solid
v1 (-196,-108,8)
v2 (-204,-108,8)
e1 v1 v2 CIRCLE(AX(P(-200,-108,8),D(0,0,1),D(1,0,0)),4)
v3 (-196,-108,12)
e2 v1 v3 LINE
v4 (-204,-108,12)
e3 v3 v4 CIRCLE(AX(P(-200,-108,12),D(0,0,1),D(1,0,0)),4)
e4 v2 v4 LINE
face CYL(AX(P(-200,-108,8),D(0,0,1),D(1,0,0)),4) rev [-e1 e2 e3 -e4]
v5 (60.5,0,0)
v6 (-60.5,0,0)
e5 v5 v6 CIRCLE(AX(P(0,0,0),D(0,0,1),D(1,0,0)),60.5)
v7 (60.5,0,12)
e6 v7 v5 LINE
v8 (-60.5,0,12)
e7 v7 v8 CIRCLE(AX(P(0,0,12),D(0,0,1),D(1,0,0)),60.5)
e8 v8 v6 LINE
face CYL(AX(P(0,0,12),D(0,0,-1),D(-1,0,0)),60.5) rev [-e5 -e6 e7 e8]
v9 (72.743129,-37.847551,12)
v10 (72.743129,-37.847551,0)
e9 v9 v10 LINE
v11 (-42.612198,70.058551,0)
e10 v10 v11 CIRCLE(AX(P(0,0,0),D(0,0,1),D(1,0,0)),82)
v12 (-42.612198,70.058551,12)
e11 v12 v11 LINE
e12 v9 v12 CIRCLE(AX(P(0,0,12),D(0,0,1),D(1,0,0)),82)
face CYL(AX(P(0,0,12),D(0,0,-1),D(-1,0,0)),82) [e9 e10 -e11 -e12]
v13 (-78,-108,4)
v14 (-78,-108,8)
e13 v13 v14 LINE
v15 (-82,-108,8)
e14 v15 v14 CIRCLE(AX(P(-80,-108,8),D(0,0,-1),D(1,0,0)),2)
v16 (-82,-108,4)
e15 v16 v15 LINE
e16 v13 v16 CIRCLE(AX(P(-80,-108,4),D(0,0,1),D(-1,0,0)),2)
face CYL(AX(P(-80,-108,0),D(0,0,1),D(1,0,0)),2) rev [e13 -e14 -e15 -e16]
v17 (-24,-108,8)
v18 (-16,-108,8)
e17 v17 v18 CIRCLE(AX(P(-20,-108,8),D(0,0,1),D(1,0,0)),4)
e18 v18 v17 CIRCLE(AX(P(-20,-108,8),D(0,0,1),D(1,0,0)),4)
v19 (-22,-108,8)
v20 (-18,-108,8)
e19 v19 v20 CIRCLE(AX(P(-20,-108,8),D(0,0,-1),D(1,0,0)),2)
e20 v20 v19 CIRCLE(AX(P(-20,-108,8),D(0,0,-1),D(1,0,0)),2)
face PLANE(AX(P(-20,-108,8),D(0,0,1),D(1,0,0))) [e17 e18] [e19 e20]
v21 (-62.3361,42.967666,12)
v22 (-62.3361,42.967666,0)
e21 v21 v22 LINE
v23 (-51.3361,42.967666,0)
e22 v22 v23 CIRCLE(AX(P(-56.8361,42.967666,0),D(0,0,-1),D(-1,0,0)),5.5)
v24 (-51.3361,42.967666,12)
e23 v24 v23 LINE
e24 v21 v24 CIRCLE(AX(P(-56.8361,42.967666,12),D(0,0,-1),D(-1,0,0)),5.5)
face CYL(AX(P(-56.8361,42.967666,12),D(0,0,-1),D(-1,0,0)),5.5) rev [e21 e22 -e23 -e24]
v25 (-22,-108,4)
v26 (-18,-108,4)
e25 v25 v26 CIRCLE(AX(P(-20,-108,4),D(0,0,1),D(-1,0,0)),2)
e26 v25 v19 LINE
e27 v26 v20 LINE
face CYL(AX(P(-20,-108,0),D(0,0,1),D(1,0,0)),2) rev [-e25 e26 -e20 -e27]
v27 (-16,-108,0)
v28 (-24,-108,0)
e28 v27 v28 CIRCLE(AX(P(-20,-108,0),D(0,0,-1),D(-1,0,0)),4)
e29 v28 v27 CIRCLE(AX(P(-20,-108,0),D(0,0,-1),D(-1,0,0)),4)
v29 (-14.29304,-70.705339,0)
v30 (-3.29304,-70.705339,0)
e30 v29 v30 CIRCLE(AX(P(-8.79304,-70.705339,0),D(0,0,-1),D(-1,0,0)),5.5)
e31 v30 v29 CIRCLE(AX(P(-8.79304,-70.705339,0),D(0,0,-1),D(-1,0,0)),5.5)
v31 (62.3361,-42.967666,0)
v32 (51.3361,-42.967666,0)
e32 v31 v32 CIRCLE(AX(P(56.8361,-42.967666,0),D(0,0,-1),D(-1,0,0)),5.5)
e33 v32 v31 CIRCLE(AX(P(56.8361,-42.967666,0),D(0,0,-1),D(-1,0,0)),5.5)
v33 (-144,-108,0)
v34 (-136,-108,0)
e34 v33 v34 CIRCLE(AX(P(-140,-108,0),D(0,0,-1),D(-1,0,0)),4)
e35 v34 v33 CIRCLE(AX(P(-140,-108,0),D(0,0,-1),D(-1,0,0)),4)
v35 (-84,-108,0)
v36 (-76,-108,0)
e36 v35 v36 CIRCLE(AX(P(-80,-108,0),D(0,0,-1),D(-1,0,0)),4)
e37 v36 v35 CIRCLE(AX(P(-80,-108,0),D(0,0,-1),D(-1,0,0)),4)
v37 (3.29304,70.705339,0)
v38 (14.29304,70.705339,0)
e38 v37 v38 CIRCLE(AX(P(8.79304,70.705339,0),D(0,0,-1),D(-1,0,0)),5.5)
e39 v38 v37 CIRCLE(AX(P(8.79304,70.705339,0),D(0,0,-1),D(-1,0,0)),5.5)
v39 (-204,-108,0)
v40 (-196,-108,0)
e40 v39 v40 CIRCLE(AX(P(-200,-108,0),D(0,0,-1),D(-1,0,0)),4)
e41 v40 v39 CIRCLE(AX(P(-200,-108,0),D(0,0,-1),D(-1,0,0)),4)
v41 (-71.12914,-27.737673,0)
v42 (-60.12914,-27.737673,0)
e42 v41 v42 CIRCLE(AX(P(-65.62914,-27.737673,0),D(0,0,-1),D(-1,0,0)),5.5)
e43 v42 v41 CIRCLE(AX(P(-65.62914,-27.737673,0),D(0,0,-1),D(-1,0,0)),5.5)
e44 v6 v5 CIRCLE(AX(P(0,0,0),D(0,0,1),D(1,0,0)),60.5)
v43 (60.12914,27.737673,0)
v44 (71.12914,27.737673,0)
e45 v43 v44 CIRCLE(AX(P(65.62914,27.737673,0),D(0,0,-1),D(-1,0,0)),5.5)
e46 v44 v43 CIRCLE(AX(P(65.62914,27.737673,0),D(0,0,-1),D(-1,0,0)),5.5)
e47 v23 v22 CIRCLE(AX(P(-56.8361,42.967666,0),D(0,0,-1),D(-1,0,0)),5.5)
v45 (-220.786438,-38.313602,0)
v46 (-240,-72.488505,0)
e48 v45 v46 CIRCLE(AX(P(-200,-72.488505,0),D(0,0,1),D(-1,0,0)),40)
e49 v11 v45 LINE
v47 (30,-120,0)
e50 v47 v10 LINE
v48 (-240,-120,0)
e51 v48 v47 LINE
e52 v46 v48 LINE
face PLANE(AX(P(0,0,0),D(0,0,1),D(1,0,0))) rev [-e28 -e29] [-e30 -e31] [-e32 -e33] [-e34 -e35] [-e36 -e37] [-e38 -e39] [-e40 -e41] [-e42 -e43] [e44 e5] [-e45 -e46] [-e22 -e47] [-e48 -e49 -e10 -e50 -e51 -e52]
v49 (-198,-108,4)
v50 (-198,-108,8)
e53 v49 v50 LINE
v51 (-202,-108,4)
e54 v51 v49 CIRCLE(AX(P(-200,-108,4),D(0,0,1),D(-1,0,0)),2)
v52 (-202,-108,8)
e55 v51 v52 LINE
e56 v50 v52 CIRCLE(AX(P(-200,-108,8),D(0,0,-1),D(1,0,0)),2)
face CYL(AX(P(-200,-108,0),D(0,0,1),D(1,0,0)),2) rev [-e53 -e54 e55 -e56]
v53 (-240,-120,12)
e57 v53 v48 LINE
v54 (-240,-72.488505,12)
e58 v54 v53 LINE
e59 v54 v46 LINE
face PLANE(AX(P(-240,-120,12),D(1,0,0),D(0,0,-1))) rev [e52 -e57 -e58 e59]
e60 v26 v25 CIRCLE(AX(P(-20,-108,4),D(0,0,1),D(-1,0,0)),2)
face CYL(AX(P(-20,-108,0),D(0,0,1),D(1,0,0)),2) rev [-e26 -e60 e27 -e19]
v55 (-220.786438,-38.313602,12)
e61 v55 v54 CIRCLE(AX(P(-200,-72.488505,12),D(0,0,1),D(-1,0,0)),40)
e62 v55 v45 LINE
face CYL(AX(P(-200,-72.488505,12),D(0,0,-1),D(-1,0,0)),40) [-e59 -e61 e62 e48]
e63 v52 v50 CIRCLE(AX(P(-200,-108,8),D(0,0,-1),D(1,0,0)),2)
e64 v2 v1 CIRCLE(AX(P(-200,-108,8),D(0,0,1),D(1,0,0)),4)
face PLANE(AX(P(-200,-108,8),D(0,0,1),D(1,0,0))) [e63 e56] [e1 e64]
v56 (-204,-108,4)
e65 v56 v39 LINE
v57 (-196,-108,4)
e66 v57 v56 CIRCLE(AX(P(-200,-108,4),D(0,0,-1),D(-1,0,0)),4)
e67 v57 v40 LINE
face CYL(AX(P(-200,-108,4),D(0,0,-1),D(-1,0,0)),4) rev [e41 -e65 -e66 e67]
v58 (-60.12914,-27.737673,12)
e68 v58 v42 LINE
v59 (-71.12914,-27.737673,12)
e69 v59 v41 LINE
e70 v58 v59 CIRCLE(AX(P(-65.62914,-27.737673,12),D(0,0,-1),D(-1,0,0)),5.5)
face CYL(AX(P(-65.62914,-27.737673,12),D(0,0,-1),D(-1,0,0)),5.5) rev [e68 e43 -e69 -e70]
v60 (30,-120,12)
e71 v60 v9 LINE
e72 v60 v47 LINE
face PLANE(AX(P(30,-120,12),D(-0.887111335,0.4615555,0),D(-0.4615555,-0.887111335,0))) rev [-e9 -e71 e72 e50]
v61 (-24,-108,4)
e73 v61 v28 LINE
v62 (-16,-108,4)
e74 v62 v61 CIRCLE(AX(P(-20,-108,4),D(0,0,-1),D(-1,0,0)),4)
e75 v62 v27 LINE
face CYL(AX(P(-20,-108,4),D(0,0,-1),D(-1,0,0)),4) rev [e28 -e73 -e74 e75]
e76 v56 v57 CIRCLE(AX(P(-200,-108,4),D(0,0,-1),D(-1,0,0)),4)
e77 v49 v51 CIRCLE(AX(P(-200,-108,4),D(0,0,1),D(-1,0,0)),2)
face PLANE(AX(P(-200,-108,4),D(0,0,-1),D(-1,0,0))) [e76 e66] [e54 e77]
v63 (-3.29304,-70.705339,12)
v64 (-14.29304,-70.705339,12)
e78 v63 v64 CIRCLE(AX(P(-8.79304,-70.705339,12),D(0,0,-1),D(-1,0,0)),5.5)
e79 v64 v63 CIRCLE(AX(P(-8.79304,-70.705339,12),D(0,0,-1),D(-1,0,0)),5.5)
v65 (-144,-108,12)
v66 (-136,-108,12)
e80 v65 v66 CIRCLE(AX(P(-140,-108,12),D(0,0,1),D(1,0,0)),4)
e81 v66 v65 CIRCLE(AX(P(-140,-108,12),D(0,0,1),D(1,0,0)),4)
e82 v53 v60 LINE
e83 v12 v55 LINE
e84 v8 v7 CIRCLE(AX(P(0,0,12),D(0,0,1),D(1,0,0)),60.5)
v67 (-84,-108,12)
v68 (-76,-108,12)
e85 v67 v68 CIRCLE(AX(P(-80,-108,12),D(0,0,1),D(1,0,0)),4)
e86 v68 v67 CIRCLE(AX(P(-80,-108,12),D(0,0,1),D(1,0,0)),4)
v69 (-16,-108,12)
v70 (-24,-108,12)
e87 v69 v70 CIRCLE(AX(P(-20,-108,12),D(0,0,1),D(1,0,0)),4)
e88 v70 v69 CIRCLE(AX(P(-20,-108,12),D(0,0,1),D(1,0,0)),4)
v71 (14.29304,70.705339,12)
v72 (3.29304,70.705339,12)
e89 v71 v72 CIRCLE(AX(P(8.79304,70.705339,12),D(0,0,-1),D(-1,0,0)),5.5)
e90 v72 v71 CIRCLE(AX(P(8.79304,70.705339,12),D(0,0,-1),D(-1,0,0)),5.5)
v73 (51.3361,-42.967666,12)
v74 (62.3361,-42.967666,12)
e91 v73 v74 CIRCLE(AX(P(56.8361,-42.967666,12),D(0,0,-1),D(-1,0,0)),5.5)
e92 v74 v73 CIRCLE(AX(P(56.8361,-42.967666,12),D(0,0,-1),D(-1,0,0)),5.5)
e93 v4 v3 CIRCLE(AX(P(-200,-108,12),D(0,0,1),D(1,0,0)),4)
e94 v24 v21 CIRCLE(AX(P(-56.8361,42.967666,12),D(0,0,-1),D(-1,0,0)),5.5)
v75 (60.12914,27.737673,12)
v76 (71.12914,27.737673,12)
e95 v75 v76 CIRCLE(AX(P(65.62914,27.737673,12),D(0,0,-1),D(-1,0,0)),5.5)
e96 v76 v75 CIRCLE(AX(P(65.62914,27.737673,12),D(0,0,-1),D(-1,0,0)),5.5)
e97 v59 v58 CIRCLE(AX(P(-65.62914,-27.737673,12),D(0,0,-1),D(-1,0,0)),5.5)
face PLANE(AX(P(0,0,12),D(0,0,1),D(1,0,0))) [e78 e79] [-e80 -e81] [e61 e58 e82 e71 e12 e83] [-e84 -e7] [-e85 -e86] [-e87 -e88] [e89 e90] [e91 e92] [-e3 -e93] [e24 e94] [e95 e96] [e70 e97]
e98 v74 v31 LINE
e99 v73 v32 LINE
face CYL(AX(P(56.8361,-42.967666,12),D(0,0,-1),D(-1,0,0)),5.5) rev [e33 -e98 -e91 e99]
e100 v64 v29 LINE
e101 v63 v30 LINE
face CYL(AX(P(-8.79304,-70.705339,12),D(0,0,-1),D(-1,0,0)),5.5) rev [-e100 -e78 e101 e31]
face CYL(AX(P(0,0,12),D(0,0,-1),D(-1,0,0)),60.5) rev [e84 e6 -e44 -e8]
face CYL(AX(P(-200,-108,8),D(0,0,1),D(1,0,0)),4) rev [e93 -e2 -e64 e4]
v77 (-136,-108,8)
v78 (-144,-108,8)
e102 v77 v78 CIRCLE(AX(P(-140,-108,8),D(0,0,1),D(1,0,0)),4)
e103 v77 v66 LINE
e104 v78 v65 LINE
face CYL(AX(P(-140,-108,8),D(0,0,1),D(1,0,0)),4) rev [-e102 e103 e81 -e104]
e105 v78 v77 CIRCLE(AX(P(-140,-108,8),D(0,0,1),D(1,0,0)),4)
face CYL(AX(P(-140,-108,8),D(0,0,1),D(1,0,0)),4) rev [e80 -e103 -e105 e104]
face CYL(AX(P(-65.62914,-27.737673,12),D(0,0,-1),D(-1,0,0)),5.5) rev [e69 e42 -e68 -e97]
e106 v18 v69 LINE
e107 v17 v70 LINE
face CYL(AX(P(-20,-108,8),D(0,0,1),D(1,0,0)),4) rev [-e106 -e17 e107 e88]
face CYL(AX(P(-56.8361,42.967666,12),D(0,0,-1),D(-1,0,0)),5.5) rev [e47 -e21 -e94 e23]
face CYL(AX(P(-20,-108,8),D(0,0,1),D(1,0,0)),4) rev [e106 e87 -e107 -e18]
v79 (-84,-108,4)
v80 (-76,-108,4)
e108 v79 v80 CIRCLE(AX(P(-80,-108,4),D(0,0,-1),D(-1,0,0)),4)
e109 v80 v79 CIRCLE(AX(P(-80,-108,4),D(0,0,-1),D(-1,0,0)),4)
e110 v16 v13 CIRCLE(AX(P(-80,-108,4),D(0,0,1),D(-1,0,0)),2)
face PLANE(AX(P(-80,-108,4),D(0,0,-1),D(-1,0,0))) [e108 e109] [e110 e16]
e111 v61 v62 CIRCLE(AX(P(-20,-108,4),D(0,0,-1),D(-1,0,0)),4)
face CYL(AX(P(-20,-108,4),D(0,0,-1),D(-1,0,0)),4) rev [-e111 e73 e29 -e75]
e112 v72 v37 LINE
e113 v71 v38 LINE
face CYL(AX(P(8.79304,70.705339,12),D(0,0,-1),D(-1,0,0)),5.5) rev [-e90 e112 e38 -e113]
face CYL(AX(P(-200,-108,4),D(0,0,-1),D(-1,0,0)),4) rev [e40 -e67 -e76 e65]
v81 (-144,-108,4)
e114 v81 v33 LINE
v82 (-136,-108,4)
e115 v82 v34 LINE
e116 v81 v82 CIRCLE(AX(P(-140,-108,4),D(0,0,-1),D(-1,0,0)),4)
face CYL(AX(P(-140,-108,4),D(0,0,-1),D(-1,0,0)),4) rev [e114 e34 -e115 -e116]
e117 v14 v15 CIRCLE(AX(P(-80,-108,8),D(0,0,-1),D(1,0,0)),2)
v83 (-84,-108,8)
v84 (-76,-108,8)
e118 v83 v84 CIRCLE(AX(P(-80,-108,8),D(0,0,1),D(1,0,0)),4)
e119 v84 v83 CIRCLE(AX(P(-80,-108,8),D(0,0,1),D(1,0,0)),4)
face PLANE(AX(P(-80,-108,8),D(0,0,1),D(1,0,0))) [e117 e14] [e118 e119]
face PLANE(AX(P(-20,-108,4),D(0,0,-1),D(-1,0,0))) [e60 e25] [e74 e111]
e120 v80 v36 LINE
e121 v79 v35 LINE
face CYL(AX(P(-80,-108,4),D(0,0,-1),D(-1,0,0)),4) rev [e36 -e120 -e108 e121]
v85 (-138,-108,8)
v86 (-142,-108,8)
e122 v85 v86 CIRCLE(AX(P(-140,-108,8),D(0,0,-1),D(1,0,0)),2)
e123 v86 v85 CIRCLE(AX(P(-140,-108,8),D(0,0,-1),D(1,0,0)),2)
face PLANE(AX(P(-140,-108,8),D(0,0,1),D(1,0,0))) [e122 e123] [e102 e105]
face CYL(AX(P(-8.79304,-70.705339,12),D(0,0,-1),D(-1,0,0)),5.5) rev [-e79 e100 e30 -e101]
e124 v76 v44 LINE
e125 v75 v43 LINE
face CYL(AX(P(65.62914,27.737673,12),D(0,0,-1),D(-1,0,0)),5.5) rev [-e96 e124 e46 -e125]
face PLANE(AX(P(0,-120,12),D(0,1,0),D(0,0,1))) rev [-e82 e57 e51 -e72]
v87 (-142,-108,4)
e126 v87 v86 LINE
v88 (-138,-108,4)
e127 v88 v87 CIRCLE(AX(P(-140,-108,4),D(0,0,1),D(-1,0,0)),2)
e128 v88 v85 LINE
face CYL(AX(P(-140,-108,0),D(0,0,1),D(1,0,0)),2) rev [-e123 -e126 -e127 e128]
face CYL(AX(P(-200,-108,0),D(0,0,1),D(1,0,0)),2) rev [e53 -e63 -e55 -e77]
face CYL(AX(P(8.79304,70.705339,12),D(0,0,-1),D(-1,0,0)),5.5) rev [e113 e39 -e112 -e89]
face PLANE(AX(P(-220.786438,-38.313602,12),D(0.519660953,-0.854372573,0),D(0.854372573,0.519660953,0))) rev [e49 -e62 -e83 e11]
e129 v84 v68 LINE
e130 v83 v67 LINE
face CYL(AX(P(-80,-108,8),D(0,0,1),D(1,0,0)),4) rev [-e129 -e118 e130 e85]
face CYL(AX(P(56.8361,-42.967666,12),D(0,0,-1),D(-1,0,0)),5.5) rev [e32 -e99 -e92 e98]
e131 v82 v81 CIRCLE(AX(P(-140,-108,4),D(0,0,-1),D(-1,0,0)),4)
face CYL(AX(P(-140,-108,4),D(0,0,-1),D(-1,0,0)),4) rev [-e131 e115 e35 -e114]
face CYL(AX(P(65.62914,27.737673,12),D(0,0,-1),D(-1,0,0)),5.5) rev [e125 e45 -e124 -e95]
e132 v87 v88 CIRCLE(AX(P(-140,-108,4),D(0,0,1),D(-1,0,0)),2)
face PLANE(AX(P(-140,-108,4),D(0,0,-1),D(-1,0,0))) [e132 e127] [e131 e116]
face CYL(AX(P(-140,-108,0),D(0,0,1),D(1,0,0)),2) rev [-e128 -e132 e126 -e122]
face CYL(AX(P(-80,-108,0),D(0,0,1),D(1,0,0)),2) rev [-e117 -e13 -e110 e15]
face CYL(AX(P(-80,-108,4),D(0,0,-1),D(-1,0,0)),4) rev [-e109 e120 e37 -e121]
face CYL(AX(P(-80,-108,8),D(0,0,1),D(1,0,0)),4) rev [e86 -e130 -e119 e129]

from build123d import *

# Parameters (mm, degrees)
EXTRUDE_1_DEPTH     = 12
SKETCH_2_R          = 60.5
CUT_EXTRUDE_2_DEPTH = 269.596351427
SKETCH_3_R          = 2
CUT_EXTRUDE_3_DEPTH = 269.596351427
SKETCH_4_R          = 4
CUT_EXTRUDE_4_DEPTH = 4
CUT_EXTRUDE_START   = -4
SKETCH_5_R          = 4
CUT_EXTRUDE_5_DEPTH = 4
SKETCH_6_R          = 5.5
CUT_EXTRUDE_6_DEPTH = 269.596351427


with BuildPart() as part:
    # 草图1 → 凸台-拉伸1 (new body)
    with BuildSketch(Plane.XY):
        with BuildLine():
            Line((0, -120), (-240, -120))
            Line((-240, -120), (-240, -72.488505))
            ThreePointArc((-240, -72.488505), (-234.867302193, -52.885667507), (-220.786438112, -38.313602065))
            Line((-220.786438112, -38.313602065), (-42.612198129, 70.058551017))
            ThreePointArc((-42.612198129, 70.058551017), (56.016961424, 59.884054913), (72.743129476, -37.847550964))
            Line((72.743129476, -37.847550964), (30, -120))
            Line((30, -120), (0, -120))
        make_face()
    extrude(amount=EXTRUDE_1_DEPTH)

    # 草图2 → 切除-拉伸2 (cut, through all)
    with BuildSketch(Plane.XY):
        Circle(SKETCH_2_R)
    extrude(amount=CUT_EXTRUDE_2_DEPTH, mode=Mode.SUBTRACT)

    # 草图3 → 切除-拉伸3 (cut, through all)
    with BuildSketch(Plane.XY.offset(12)):
        with Locations((-200, -108)):
            Circle(SKETCH_3_R)
        with Locations((-140, -108)):
            Circle(SKETCH_3_R)
        with Locations((-80, -108)):
            Circle(SKETCH_3_R)
        with Locations((-20, -108)):
            Circle(SKETCH_3_R)
    extrude(amount=-CUT_EXTRUDE_3_DEPTH, mode=Mode.SUBTRACT)

    # 草图4 → 切除-拉伸4 (cut)
    with BuildSketch(Plane.XY.offset(12)):
        with Locations((-200, -108)):
            Circle(SKETCH_4_R)
        with Locations((-140, -108)):
            Circle(SKETCH_4_R)
        with Locations((-80, -108)):
            Circle(SKETCH_4_R)
        with Locations((-20, -108)):
            Circle(SKETCH_4_R)
    extrude(amount=-CUT_EXTRUDE_4_DEPTH, mode=Mode.SUBTRACT)

    # 草图5 → 切除-拉伸5 (cut)
    with BuildSketch(Plane(origin=(0, 0, 0), x_dir=(-1, 0, 0), z_dir=(0, 0, -1)).offset(CUT_EXTRUDE_START)):
        with Locations(Location((20, -108, 0), (0, 0, 180))):
            Circle(SKETCH_5_R)
        with Locations(Location((80, -108, 0), (0, 0, 180))):
            Circle(SKETCH_5_R)
        with Locations(Location((140, -108, 0), (0, 0, 180))):
            Circle(SKETCH_5_R)
        with Locations(Location((200, -108, 0), (0, 0, 180))):
            Circle(SKETCH_5_R)
    extrude(amount=CUT_EXTRUDE_5_DEPTH, mode=Mode.SUBTRACT)

    # 草图6 → 切除-拉伸6 (cut, through all)
    with BuildSketch(Plane(origin=(0, 0, 0), x_dir=(-1, 0, 0), z_dir=(0, 0, -1))):
        with Locations((56.836099532, 42.967665634)):
            Circle(SKETCH_6_R)
        with Locations((-8.793040215, 70.705338863)):
            Circle(SKETCH_6_R)
        with Locations((65.629139746, -27.737673229)):
            Circle(SKETCH_6_R)
        with Locations((8.793040215, -70.705338863)):
            Circle(SKETCH_6_R)
        with Locations((-56.836099532, -42.967665634)):
            Circle(SKETCH_6_R)
        with Locations((-65.629139746, 27.737673229)):
            Circle(SKETCH_6_R)
    extrude(amount=-CUT_EXTRUDE_6_DEPTH, mode=Mode.SUBTRACT)


solid = part.part
